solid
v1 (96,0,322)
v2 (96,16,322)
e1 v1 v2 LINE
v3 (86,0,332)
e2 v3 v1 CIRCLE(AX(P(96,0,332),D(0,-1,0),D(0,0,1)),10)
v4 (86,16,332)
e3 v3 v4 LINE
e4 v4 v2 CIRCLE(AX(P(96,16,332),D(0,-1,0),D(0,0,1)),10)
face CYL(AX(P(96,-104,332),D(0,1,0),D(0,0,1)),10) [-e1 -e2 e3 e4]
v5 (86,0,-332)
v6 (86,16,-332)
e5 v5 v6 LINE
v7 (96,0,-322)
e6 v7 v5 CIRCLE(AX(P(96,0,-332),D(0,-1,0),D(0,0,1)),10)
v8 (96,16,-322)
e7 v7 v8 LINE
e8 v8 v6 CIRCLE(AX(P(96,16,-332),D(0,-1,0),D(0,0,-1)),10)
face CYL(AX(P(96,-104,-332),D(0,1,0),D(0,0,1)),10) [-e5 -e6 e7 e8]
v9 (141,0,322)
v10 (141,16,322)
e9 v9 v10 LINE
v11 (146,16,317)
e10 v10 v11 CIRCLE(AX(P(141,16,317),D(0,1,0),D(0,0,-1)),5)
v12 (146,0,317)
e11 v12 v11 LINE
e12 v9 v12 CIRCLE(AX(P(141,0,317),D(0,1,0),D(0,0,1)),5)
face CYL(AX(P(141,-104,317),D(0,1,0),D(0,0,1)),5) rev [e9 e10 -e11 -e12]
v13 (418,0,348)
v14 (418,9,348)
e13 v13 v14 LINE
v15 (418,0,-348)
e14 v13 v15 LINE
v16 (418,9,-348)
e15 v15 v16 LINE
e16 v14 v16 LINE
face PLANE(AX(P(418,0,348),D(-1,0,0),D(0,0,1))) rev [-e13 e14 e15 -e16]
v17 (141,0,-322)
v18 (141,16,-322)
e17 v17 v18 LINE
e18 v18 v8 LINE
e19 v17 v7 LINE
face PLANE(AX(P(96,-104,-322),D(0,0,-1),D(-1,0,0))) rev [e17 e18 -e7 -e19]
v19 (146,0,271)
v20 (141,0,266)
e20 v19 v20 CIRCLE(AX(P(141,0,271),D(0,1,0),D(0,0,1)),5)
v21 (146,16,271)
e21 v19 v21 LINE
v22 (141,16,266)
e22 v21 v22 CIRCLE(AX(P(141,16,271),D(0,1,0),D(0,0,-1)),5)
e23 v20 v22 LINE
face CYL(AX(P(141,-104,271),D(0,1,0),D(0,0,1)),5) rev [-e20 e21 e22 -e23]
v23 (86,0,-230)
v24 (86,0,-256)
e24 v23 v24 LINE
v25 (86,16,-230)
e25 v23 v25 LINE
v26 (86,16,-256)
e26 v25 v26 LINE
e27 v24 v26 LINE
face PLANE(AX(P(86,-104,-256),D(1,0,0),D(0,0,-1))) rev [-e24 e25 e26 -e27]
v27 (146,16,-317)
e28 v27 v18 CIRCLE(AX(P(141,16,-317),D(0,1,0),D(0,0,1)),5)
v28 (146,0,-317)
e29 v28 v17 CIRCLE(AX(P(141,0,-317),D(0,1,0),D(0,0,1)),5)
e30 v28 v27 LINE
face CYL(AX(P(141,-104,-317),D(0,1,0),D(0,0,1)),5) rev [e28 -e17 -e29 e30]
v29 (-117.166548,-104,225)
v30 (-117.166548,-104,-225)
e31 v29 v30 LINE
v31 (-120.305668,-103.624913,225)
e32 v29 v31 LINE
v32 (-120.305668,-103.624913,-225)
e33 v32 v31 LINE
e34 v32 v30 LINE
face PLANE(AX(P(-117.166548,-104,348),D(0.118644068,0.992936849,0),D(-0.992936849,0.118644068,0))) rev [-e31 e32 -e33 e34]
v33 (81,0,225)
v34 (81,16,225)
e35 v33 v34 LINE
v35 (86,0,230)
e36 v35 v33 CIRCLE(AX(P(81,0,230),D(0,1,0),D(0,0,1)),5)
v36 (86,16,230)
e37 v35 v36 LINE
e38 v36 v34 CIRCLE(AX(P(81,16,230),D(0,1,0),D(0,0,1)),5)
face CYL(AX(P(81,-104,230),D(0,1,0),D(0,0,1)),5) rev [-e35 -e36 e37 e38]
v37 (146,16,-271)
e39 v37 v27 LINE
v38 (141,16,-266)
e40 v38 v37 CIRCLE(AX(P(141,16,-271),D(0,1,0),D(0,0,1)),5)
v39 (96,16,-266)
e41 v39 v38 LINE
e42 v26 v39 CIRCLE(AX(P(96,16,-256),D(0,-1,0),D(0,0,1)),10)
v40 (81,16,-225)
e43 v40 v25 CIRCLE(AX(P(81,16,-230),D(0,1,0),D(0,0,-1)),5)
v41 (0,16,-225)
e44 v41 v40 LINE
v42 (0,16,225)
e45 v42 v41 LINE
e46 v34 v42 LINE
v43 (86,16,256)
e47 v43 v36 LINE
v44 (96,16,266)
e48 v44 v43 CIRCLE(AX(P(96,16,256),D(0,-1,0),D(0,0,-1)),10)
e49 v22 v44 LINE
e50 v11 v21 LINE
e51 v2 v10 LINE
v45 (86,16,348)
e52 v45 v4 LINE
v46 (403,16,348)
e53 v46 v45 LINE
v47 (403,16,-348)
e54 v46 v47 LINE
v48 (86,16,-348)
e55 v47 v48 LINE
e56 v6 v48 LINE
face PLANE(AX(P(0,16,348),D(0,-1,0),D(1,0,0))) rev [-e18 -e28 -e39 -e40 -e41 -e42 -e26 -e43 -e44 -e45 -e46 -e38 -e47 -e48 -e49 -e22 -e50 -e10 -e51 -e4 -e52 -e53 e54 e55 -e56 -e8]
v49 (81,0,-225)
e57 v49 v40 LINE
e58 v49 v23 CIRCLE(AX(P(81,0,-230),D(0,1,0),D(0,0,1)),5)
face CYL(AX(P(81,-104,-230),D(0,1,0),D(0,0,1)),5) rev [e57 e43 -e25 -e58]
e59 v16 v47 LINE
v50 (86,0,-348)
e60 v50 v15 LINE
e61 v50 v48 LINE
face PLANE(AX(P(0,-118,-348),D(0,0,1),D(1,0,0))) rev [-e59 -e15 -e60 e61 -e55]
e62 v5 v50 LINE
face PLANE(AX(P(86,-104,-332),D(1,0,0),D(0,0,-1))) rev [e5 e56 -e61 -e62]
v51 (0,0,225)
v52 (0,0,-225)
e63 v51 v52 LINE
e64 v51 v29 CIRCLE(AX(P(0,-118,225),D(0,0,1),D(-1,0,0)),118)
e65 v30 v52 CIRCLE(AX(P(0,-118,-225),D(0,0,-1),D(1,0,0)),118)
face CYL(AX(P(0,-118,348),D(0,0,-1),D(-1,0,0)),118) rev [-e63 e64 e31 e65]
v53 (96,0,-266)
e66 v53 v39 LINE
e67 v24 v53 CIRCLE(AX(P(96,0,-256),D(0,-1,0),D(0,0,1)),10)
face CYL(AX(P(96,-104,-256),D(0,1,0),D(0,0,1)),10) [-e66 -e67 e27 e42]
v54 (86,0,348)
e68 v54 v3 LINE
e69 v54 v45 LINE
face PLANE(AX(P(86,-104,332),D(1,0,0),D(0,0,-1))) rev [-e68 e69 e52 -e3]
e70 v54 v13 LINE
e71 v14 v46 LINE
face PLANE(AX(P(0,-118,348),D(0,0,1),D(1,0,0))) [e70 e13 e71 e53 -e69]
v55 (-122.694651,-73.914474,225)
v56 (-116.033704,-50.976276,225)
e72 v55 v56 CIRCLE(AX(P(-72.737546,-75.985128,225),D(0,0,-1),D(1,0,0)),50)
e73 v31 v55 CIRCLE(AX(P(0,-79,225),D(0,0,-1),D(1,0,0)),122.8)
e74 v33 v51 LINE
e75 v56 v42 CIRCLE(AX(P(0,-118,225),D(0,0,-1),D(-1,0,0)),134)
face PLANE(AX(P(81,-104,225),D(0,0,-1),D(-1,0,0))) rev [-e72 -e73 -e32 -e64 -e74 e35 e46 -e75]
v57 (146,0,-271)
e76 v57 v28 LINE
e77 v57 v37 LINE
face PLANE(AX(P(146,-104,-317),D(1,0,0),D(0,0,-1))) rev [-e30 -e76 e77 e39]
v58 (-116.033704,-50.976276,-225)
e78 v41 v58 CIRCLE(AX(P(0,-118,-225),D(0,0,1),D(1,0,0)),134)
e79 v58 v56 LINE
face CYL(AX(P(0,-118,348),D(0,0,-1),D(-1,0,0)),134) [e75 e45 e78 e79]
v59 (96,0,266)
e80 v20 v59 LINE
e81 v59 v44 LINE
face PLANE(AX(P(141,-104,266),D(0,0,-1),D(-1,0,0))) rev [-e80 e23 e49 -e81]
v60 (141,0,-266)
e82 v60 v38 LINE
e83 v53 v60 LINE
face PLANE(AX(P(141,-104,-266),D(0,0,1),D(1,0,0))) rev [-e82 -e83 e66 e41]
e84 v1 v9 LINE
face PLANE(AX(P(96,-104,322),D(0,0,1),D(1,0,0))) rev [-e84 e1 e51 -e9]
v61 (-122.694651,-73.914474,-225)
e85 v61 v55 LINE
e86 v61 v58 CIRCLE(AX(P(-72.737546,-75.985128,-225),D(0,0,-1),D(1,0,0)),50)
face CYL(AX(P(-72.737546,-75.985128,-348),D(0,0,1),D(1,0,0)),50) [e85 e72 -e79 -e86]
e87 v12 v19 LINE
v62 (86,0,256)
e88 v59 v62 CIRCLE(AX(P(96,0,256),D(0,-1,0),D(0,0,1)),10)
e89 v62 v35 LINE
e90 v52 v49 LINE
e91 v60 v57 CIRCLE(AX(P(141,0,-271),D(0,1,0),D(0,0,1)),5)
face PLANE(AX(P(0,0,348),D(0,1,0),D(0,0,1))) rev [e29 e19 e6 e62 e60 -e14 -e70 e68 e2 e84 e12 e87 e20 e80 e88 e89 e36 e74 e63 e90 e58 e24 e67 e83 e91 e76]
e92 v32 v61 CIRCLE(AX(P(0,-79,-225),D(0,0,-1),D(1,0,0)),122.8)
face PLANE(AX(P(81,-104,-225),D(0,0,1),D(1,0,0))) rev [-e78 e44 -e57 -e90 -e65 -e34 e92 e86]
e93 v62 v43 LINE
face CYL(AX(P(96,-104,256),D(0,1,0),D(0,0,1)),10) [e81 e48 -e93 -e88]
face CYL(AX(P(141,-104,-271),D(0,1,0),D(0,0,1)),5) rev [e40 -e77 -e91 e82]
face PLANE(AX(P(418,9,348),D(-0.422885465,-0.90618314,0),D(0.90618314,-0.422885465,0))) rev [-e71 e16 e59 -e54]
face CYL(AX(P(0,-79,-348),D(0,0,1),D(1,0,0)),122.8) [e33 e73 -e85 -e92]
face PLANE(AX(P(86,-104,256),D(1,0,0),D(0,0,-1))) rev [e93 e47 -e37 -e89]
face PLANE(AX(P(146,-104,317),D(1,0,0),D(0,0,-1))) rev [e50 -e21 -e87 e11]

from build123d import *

# Parameters (mm, degrees)
BOSS_EXTRUDE1_DEPTH     = 348
CUT_EXTRUDE1_DEPTH      = 554.754458221
CUT_EXTRUDE1_DEPTH_BACK = 554.754458221
CUT_EXTRUDE3_DEPTH      = 717.846566568


with BuildPart() as part:
    # Sketch1 → Boss-Extrude1 (new, symmetric)
    with BuildSketch(Plane.XY):
        with BuildLine():
            Line((0, 0), (418, 0))
            Line((418, 0), (418, 9))
            Line((418, 9), (403, 16))
            Line((403, 16), (0, 16))
            ThreePointArc((0, 16), (-88.953996871, -17.784300428), (-133.053537704, -102.101694915))
            Line((-133.053537704, -102.101694915), (-117.166548127, -104))
            ThreePointArc((-117.166548127, -104), (-78.33262411, -29.750354108), (0, 0))
        make_face()
    extrude(amount=BOSS_EXTRUDE1_DEPTH, both=True)

    # Sketch2 → Cut-Extrude1 (cut, two sides: drawn at the far end of the back side and taken through both)
    with BuildSketch(Plane(origin=(0, 0, 0), x_dir=(1, 0, 0), z_dir=(0, 1, 0)).offset(-CUT_EXTRUDE1_DEPTH_BACK)):
        with BuildLine():
            Line((86, -256), (86, -230))
            ThreePointArc((86, -230), (84.535533906, -226.464466094), (81, -225))
            Line((81, -225), (-133.053537704, -225))
            Line((-133.053537704, -225), (-133.053537704, -348))
            Line((-133.053537704, -348), (86, -348))
            Line((86, -348), (86, -332))
            ThreePointArc((86, -332), (88.928932188, -324.928932188), (96, -322))
            Line((96, -322), (141, -322))
            ThreePointArc((141, -322), (144.535533906, -320.535533906), (146, -317))
            Line((146, -317), (146, -271))
            ThreePointArc((146, -271), (144.535533906, -267.464466094), (141, -266))
            Line((141, -266), (96, -266))
            ThreePointArc((96, -266), (88.928932188, -263.071067812), (86, -256))
        make_face()
        with BuildLine():
            Line((96, 322), (141, 322))
            ThreePointArc((141, 322), (144.535533906, 320.535533906), (146, 317))
            Line((146, 317), (146, 271))
            ThreePointArc((146, 271), (144.535533906, 267.464466094), (141, 266))
            Line((141, 266), (96, 266))
            ThreePointArc((96, 266), (88.928932188, 263.071067812), (86, 256))
            Line((86, 256), (86, 230))
            ThreePointArc((86, 230), (84.535533906, 226.464466094), (81, 225))
            Line((81, 225), (-133.053537704, 225))
            Line((-133.053537704, 225), (-133.053537704, 348))
            Line((-133.053537704, 348), (86, 348))
            Line((86, 348), (86, 332))
            ThreePointArc((86, 332), (88.928932188, 324.928932188), (96, 322))
        make_face()
    extrude(amount=CUT_EXTRUDE1_DEPTH + CUT_EXTRUDE1_DEPTH_BACK, mode=Mode.SUBTRACT)

    # Sketch3 → Cut-Extrude3 (cut, through all)
    with BuildSketch(Plane.XY.offset(225)):
        with BuildLine():
            Line((-120.305667655, -103.624912792), (-133.053537704, -102.101694915))
            ThreePointArc((-133.053537704, -102.101694915), (-127.139944881, -75.674659886), (-116.033703785, -50.976275946))
            ThreePointArc((-116.033703785, -50.976275946), (-120.754032763, -62.041779759), (-122.694651189, -73.9144745))
            ThreePointArc((-122.694651189, -73.9144745), (-122.404927497, -88.842445048), (-120.305667655, -103.624912792))
        make_face()
    extrude(amount=-CUT_EXTRUDE3_DEPTH, mode=Mode.SUBTRACT)


solid = part.part
